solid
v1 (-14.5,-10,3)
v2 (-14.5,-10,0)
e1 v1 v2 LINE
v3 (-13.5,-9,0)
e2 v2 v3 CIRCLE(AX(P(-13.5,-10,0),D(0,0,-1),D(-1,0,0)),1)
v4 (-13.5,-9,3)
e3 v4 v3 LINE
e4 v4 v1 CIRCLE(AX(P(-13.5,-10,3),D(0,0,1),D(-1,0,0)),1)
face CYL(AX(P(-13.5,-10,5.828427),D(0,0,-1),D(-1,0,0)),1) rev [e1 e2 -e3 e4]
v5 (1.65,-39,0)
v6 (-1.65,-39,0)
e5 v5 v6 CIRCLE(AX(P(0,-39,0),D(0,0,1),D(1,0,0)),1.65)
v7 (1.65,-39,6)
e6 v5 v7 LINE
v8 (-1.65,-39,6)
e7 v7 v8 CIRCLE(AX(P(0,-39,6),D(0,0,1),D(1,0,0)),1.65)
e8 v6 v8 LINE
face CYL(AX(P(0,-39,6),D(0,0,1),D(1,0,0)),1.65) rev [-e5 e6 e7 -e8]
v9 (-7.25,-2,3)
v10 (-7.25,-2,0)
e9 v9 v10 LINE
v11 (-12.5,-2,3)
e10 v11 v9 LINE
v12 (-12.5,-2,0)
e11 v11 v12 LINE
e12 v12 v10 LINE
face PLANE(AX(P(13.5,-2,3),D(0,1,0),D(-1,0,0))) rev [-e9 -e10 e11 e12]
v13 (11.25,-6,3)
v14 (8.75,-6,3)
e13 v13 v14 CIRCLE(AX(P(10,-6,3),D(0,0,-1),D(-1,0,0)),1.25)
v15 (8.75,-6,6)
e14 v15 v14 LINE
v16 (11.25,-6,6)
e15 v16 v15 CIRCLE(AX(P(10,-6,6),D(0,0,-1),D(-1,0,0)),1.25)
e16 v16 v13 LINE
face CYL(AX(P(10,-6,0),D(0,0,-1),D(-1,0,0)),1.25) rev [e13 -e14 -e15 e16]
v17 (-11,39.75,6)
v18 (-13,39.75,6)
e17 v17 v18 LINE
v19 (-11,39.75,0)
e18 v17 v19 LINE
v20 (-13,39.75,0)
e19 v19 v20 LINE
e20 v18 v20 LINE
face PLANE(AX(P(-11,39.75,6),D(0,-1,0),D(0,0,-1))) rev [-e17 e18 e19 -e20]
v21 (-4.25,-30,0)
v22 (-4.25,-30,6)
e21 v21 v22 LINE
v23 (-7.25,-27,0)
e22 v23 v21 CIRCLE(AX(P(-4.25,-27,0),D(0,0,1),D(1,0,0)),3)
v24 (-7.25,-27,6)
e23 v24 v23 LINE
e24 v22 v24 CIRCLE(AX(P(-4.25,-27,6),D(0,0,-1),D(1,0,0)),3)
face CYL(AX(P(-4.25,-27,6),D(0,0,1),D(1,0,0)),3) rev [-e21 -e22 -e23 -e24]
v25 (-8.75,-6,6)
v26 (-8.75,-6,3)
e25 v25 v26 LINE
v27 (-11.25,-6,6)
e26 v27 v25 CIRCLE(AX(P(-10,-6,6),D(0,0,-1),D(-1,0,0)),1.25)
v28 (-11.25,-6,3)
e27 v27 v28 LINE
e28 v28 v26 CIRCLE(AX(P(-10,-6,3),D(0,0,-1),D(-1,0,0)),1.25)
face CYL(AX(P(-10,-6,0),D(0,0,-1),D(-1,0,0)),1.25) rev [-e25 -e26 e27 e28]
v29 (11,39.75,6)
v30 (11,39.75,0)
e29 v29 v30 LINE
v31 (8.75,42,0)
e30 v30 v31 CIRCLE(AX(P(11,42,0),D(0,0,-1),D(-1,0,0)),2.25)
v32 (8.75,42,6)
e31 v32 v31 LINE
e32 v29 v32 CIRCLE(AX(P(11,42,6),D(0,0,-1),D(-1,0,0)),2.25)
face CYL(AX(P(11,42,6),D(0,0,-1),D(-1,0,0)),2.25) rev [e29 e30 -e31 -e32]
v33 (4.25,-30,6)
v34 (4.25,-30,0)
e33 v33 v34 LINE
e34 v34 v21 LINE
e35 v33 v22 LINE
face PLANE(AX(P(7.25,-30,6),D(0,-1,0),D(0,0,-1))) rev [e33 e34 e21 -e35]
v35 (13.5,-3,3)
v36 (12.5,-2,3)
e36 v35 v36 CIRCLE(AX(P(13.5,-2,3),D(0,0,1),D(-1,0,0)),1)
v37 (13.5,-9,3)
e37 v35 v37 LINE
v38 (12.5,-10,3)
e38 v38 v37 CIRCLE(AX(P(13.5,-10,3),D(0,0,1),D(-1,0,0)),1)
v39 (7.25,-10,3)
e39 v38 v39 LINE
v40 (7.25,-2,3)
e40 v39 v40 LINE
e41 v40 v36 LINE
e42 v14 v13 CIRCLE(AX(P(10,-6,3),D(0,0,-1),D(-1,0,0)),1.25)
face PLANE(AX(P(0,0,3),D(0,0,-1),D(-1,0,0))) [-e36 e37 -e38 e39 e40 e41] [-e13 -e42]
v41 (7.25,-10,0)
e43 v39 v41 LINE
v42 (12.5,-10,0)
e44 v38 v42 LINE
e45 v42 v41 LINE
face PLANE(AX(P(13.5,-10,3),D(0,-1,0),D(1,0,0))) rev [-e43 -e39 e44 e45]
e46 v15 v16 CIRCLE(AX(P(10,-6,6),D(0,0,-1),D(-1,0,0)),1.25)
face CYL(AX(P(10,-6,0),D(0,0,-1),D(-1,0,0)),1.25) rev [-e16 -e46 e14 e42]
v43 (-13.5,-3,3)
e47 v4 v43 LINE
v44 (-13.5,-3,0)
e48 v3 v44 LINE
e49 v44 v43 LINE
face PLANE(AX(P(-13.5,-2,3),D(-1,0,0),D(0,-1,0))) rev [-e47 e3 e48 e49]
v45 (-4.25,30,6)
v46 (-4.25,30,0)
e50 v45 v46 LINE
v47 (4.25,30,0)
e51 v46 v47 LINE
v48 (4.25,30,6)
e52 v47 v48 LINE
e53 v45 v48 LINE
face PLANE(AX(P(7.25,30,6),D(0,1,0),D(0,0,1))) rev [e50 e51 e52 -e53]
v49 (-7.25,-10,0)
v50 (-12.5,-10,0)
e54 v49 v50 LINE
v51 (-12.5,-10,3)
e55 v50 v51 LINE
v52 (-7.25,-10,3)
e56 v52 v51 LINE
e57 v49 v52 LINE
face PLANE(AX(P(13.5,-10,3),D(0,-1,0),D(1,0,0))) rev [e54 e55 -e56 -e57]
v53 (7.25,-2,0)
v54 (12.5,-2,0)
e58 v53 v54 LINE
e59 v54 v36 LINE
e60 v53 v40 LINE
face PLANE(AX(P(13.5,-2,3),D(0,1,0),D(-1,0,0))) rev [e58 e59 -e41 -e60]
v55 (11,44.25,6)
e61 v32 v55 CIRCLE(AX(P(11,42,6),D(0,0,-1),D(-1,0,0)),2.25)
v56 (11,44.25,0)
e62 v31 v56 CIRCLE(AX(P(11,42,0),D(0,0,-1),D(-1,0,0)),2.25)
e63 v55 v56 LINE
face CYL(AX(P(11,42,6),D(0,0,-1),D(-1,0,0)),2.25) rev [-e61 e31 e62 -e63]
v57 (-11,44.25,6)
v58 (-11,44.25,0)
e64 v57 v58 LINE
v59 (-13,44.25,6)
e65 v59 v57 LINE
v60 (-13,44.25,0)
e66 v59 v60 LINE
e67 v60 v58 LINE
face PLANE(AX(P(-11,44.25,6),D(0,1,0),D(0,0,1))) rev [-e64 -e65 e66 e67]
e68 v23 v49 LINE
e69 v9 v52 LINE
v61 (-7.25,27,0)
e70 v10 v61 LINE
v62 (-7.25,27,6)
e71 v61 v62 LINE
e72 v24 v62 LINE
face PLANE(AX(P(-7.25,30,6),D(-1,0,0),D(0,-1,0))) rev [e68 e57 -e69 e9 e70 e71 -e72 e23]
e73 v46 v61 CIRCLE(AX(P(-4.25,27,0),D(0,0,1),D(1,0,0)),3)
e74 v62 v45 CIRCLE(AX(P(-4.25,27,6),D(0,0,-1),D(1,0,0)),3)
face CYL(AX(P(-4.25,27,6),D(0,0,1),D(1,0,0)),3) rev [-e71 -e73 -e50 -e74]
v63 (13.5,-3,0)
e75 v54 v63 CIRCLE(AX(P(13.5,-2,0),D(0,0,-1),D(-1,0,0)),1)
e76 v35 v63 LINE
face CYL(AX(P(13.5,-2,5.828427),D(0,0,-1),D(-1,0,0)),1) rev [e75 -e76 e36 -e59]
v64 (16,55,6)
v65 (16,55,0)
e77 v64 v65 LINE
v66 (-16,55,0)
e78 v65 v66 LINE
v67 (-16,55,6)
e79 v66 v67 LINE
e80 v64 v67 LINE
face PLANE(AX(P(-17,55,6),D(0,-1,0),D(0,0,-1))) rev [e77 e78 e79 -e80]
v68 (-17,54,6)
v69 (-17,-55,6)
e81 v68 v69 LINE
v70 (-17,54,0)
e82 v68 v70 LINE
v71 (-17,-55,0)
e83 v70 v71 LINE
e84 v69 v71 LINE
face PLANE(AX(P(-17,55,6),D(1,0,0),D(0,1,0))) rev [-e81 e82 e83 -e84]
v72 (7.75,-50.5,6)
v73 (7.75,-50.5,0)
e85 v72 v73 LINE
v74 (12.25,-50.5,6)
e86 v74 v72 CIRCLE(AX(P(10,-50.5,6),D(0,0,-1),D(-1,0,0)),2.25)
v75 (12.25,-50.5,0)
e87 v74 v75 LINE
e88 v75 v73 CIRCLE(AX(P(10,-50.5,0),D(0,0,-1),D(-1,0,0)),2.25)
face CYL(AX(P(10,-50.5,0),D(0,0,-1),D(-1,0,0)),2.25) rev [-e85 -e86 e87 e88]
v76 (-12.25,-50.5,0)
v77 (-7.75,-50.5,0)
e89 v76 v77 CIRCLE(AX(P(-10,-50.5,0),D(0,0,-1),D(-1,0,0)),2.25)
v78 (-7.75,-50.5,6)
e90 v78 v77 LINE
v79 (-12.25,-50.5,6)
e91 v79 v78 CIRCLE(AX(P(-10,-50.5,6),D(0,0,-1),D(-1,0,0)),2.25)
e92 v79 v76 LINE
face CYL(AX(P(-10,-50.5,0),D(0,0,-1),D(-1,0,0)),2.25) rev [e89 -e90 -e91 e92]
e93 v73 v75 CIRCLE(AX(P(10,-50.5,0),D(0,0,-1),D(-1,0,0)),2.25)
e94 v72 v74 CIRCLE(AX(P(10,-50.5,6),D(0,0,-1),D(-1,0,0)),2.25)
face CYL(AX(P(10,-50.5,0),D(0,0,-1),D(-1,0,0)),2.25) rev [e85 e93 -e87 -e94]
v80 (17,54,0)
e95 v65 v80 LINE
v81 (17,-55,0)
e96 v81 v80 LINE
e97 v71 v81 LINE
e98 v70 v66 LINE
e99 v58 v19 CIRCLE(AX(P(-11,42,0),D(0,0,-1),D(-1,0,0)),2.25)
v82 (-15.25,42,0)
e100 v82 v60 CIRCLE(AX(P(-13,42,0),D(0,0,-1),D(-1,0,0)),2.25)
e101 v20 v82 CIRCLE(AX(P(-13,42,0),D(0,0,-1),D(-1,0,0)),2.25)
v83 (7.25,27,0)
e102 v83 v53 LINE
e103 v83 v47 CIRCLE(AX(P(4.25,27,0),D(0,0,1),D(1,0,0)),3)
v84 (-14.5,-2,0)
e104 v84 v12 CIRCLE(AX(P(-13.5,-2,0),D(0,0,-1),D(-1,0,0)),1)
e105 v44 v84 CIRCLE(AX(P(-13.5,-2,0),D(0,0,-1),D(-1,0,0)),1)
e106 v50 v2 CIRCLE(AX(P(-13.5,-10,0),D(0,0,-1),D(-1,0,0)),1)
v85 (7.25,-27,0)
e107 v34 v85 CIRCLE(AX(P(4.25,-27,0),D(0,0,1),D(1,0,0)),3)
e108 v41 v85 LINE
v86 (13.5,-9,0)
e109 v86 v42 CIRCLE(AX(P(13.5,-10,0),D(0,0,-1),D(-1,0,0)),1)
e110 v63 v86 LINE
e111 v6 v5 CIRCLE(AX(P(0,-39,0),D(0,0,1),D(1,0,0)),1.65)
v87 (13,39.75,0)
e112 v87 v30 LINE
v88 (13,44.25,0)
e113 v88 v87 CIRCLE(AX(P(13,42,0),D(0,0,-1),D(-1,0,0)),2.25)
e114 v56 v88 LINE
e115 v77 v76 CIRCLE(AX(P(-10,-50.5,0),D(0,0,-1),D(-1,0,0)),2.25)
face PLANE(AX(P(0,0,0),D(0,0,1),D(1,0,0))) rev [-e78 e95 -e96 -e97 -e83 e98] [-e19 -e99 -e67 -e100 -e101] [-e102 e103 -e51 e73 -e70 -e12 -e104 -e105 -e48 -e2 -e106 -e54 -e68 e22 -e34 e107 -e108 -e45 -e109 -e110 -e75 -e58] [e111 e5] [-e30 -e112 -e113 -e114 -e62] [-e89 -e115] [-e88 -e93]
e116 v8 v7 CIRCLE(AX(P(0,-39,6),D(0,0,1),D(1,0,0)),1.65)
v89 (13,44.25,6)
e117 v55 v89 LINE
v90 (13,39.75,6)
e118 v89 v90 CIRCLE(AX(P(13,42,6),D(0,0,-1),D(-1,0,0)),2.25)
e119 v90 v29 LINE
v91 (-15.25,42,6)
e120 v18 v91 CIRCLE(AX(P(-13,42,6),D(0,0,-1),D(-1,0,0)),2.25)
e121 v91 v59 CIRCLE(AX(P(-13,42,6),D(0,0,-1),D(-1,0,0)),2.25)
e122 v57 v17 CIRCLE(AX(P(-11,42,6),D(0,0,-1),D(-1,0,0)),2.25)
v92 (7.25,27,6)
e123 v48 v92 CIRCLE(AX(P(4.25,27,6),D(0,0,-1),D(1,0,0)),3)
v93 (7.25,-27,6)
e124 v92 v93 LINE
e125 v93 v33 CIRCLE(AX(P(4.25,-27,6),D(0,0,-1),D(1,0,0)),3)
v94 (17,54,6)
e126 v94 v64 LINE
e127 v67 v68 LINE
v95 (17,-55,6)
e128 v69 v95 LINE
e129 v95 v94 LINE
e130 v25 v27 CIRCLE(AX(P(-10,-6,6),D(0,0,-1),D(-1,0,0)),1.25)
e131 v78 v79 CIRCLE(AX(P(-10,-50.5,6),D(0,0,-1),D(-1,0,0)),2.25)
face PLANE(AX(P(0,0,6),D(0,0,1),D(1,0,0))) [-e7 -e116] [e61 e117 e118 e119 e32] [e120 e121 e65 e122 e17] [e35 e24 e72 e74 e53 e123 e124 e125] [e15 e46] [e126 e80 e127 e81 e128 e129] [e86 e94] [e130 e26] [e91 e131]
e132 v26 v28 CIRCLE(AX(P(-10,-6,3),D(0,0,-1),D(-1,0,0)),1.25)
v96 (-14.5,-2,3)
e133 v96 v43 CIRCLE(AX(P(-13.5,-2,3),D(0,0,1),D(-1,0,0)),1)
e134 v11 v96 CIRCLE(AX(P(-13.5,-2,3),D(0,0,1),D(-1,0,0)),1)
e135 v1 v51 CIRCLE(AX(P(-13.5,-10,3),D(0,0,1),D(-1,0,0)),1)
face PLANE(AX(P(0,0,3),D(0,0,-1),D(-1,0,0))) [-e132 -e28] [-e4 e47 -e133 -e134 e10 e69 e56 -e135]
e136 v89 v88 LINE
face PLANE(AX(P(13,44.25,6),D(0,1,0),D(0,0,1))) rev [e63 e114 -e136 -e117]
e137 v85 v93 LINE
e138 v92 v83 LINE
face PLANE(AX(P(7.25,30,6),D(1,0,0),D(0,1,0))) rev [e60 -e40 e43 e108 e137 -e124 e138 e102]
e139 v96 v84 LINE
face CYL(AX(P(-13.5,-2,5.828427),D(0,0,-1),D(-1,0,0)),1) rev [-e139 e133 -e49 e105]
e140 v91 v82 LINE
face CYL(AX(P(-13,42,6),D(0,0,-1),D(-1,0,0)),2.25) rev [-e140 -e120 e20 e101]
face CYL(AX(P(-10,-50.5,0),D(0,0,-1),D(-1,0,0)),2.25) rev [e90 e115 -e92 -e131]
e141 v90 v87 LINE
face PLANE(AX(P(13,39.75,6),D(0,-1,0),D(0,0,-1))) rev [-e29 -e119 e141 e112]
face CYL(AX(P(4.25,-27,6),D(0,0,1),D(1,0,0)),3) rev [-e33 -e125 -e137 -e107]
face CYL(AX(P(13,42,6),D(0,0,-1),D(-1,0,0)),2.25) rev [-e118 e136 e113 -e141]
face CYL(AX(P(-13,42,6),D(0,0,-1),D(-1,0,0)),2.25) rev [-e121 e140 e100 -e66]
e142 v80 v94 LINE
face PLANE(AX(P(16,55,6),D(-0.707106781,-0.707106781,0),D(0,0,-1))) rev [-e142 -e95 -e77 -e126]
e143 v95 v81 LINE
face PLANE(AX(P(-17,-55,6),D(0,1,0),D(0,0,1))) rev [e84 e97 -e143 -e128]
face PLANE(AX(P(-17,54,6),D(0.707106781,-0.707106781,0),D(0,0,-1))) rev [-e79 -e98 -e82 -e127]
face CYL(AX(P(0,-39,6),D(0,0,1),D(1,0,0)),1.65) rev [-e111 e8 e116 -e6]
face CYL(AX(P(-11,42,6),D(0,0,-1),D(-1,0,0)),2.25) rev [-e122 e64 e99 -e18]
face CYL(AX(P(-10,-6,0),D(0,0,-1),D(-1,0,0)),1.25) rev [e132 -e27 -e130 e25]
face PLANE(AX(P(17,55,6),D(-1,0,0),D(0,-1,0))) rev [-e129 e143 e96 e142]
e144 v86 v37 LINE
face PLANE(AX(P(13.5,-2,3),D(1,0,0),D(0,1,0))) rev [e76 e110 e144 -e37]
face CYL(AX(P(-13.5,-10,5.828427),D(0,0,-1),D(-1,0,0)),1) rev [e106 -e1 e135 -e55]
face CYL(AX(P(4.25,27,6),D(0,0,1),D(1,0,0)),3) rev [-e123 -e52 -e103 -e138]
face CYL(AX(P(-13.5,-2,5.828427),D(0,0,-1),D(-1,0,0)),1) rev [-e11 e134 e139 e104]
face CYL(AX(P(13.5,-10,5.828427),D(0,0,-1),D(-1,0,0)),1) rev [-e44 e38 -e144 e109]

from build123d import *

# Parameters (mm, degrees)
SKETCH1_W                  = 34
SKETCH1_H                  = 110
BOSS_EXTRUDE1_DEPTH        = 6
CHAMFER1_SIZE              = 1
F_4_5_4_5_DIAMETER_HOLE1_D = 4.5
CUT_EXTRUDE1_DEPTH         = 58.879184514
SKETCH12_W                 = 14.5
SKETCH12_H                 = 60
CUT_EXTRUDE2_DEPTH         = 58.879184514
SKETCH13_W                 = 27
SKETCH13_H                 = 8
CUT_EXTRUDE3_DEPTH         = 3
FILLET1_R                  = 3
SKETCH14_R                 = 1
CUT_EXTRUDE4_DEPTH         = 3
M3_TAPPED_HOLE1_D          = 2.5
M4_TAPPED_HOLE1_D          = 3.3


with BuildPart() as part:
    # Sketch1 → Boss-Extrude1 (new body)
    with BuildSketch(Plane.XY):
        Rectangle(SKETCH1_W, SKETCH1_H)
    extrude(amount=BOSS_EXTRUDE1_DEPTH)

    # Chamfer1
    chamfer1_edges = [part.edges().sort_by_distance(p)[0] for p in [
        (-17, 55, 3),
        (17, 55, 3),
    ]]
    chamfer(chamfer1_edges, length=CHAMFER1_SIZE)

    # Ø4.5 (4.5) Diameter Hole1 (through all)
    with Locations(Plane(origin=(0, 0, 0), x_dir=(-1, 0, 0), z_dir=(0, 0, -1))):
        with Locations((-10, -50.5), (10, -50.5)):
            Hole(F_4_5_4_5_DIAMETER_HOLE1_D / 2)

    # Sketch4 → Cut-Extrude1 (cut, through all)
    with BuildSketch(Plane(origin=(0, 0, 0), x_dir=(-1, 0, 0), z_dir=(0, 0, -1))):
        with BuildLine():
            Line((-13, 44.25), (-11, 44.25))
            ThreePointArc((-11, 44.25), (-8.75, 42), (-11, 39.75))
            Line((-11, 39.75), (-13, 39.75))
            ThreePointArc((-13, 39.75), (-15.25, 42), (-13, 44.25))
        make_face()
        with BuildLine():
            Line((11, 44.25), (13, 44.25))
            ThreePointArc((13, 44.25), (15.25, 42), (13, 39.75))
            Line((13, 39.75), (11, 39.75))
            ThreePointArc((11, 39.75), (8.75, 42), (11, 44.25))
        make_face()
    extrude(amount=-CUT_EXTRUDE1_DEPTH, mode=Mode.SUBTRACT)

    # Sketch12 → Cut-Extrude2 (cut, through all)
    with BuildSketch(Plane(origin=(0, 0, 0), x_dir=(-1, 0, 0), z_dir=(0, 0, -1))):
        Rectangle(SKETCH12_W, SKETCH12_H)
    extrude(amount=-CUT_EXTRUDE2_DEPTH, mode=Mode.SUBTRACT)

    # Sketch13 → Cut-Extrude3 (cut)
    with BuildSketch(Plane(origin=(0, 0, 0), x_dir=(-1, 0, 0), z_dir=(0, 0, -1))):
        with Locations((0, -6)):
            Rectangle(SKETCH13_W, SKETCH13_H)
    extrude(amount=-CUT_EXTRUDE3_DEPTH, mode=Mode.SUBTRACT)

    # Fillet1
    fillet1_edges = [part.edges().sort_by_distance(p)[0] for p in [
        (-7.25, 30, 3),
        (-7.25, -30, 3),
        (7.25, -30, 3),
        (7.25, 30, 3),
    ]]
    fillet(fillet1_edges, radius=FILLET1_R)

    # Sketch14 → Cut-Extrude4 (cut)
    with BuildSketch(Plane(origin=(0, 0, 0), x_dir=(-1, 0, 0), z_dir=(0, 0, -1))):
        with Locations((-13.5, -2)):
            Circle(SKETCH14_R)
        with Locations((-13.5, -10)):
            Circle(SKETCH14_R)
        with Locations((13.5, -10)):
            Circle(SKETCH14_R)
        with Locations((13.5, -2)):
            Circle(SKETCH14_R)
    extrude(amount=-CUT_EXTRUDE4_DEPTH, mode=Mode.SUBTRACT)

    # M3 Tapped Hole1 (through all)
    with Locations(Plane(origin=(0, 0, 0), x_dir=(-1, 0, 0), z_dir=(0, 0, -1))):
        with Locations((-10, -6), (10, -6)):
            Hole(M3_TAPPED_HOLE1_D / 2)

    # M4 Tapped Hole1 (through all)
    with Locations(Plane.XY.offset(6)):
        with Locations((0, -39)):
            Hole(M4_TAPPED_HOLE1_D / 2)


solid = part.part
